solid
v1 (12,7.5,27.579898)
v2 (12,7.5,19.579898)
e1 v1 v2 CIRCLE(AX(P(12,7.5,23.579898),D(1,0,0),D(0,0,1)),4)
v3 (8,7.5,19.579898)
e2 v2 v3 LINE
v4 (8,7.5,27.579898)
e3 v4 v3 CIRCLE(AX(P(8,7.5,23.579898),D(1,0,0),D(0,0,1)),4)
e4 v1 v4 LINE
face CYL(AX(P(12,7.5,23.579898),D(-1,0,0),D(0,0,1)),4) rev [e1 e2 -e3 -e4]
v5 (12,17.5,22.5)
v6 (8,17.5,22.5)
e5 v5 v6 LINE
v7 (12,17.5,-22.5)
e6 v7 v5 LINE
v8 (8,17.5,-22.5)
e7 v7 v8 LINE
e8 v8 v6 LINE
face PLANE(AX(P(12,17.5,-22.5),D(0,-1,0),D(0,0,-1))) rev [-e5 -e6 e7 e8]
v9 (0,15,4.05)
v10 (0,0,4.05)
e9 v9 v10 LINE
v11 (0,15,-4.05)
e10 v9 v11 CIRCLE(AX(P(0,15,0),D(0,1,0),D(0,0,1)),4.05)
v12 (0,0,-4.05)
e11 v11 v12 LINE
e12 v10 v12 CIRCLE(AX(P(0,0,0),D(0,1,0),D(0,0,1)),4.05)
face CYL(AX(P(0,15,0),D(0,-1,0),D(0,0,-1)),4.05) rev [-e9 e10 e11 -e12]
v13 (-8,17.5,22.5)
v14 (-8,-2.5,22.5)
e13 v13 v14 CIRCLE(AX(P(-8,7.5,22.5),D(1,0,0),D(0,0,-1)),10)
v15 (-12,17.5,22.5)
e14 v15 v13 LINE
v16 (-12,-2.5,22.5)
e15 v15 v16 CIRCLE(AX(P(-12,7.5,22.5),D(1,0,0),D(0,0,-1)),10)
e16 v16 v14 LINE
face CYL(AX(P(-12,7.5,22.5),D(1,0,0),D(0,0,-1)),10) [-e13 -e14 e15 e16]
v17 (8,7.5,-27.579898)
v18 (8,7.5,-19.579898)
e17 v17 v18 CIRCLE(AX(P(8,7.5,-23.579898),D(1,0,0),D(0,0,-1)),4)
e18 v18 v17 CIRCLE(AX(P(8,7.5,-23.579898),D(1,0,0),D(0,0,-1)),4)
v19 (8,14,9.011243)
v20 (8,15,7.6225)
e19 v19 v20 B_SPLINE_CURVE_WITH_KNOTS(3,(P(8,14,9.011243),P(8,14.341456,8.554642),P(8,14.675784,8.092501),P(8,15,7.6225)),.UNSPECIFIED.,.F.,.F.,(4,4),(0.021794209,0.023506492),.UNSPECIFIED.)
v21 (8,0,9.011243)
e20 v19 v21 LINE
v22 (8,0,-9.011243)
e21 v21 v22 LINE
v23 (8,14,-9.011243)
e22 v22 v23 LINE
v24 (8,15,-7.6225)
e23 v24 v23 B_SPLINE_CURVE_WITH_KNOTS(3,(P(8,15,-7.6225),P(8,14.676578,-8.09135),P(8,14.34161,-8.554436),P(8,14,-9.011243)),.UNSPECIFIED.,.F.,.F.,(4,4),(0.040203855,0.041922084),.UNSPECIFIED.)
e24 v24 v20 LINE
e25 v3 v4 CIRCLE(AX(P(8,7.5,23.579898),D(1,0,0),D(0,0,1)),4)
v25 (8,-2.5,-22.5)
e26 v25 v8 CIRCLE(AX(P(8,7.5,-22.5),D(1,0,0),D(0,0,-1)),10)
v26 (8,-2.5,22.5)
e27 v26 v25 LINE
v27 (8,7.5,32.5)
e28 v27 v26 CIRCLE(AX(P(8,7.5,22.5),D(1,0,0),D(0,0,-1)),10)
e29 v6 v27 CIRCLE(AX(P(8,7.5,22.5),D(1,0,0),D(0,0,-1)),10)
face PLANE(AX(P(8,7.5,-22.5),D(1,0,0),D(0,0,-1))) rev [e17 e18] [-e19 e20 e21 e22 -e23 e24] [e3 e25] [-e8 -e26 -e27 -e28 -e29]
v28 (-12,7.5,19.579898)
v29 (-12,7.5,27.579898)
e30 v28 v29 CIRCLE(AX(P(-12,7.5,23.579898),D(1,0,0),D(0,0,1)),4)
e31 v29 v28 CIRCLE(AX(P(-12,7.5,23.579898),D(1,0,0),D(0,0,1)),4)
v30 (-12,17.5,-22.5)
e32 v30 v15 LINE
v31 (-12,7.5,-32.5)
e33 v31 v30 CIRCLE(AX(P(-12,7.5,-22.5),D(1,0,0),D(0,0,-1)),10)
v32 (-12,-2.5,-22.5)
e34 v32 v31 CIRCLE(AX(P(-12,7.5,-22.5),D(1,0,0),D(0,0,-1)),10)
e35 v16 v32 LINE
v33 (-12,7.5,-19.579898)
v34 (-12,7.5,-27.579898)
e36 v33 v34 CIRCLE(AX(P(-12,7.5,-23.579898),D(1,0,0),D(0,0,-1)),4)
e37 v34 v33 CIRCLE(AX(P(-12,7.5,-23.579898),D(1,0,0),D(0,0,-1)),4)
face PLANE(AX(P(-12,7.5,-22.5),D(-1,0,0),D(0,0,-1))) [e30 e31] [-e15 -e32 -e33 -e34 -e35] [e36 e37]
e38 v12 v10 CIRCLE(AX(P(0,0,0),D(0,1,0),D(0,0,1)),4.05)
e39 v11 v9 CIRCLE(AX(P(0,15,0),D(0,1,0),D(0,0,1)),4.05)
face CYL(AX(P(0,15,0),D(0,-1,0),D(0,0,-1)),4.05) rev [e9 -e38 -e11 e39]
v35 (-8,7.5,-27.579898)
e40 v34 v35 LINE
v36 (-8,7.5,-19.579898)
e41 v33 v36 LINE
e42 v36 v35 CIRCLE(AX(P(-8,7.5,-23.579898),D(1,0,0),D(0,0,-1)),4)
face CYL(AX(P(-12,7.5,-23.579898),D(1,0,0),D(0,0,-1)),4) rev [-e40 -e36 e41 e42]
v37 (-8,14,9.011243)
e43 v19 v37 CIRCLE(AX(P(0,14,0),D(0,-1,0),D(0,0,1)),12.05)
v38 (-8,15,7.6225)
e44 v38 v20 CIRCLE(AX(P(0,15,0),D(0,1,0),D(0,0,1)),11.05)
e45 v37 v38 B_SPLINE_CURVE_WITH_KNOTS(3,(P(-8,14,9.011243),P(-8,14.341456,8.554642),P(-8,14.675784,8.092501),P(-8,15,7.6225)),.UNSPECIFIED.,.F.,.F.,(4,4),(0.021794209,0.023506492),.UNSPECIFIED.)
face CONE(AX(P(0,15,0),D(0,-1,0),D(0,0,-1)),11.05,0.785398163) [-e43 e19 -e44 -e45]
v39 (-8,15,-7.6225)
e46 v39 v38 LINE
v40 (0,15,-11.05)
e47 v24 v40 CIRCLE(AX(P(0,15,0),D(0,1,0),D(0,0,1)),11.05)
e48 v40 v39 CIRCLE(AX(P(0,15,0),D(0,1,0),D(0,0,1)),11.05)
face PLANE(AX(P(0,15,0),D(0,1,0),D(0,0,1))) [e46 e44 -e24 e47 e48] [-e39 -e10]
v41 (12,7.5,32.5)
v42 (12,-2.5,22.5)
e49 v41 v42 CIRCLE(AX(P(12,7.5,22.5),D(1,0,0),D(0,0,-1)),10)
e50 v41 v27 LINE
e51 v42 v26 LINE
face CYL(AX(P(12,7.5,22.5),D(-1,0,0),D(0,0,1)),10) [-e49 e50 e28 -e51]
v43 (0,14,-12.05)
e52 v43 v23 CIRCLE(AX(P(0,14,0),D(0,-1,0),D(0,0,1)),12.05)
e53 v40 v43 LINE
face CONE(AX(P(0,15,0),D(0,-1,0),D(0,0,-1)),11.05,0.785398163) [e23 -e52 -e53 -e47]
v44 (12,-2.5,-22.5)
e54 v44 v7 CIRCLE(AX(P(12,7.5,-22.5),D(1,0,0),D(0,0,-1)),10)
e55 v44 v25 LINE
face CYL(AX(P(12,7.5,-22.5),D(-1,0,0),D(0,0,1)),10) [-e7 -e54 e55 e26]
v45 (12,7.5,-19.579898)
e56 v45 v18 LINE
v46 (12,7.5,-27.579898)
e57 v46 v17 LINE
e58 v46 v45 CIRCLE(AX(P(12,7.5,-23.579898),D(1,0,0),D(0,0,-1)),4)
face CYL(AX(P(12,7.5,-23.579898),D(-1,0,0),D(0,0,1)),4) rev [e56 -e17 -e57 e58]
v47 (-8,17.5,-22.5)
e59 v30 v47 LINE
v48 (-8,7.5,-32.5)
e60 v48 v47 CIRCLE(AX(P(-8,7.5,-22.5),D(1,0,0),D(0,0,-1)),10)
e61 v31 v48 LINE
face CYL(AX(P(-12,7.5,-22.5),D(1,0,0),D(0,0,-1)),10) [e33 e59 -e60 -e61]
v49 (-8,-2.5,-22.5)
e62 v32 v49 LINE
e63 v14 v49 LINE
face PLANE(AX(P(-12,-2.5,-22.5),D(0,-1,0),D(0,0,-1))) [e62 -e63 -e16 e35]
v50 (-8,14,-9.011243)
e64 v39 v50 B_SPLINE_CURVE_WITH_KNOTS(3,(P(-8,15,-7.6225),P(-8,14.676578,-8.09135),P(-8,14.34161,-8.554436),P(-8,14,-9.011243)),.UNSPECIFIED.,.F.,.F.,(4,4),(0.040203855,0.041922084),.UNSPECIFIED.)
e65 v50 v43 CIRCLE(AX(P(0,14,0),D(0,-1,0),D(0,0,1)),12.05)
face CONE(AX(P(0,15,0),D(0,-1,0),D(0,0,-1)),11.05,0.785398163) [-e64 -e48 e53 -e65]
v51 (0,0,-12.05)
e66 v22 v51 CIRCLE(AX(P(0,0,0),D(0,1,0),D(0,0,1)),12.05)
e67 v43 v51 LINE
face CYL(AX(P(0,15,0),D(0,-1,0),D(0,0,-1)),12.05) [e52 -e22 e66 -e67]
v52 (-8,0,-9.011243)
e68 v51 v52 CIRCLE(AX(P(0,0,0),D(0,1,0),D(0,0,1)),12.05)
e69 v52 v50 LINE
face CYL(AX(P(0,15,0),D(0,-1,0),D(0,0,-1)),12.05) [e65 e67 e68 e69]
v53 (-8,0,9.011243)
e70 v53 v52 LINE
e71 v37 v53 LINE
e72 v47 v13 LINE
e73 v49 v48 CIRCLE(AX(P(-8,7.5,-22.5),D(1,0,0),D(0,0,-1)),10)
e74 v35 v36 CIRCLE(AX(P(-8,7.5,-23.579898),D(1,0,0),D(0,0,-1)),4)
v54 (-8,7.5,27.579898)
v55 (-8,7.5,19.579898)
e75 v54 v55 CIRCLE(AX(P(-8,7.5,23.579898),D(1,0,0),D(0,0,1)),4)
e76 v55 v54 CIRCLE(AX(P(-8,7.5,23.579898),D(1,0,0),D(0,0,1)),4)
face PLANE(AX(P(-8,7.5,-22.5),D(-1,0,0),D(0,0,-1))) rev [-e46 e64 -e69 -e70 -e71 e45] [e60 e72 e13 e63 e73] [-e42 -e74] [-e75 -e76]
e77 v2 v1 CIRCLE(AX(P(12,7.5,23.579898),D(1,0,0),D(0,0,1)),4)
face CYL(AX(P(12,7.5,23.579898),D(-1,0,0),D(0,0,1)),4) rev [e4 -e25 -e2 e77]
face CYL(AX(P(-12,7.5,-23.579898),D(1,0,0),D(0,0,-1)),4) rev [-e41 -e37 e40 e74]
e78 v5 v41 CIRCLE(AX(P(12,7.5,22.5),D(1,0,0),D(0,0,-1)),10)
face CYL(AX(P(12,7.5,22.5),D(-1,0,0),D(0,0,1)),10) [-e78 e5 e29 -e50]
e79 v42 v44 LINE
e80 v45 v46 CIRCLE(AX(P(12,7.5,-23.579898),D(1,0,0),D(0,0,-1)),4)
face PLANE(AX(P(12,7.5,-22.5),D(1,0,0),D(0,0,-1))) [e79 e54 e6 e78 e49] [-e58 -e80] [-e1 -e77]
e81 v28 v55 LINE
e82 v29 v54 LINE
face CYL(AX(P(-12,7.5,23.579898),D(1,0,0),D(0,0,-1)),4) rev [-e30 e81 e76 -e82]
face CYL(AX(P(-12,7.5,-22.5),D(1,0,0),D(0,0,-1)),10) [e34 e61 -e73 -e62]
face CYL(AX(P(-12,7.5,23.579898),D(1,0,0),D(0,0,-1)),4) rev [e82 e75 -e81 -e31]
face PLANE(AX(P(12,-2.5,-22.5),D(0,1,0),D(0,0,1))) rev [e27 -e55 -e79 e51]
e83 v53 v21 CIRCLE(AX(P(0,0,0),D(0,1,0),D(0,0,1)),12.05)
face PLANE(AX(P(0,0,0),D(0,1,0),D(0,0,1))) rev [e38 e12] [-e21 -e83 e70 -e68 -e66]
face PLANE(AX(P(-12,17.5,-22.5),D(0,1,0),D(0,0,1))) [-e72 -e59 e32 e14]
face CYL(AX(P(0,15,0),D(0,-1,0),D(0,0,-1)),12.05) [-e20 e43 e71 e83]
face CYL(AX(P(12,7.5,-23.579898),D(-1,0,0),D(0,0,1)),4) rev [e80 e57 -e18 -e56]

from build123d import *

# Parameters (mm, degrees)
SKETCH1_R          = 12.05
SKETCH1_R_2        = 4.05
BOSS_EXTRU_1_DEPTH = 15
CHAMFER1_SIZE      = 1
CUT_EXTRUDE1_REACH = 24.703
SKETCH5_W          = 7
SKETCH5_H          = 40.880501257
SKETCH6_R          = 4
BOSS_EXTRU_4_DEPTH = 4


with BuildPart() as part:
    # Sketch1 → Boss.-Extru.1 (new body)
    with BuildSketch(Plane(origin=(0, 0, 0), x_dir=(1, 0, 0), z_dir=(0, 1, 0))):
        with Locations(Location((0, 0, 0), (0, 0, 270))):
            Circle(SKETCH1_R)
        with Locations(Location((0, 0, 0), (0, 0, 270))):
            Circle(SKETCH1_R_2, mode=Mode.SUBTRACT)
    extrude(amount=BOSS_EXTRU_1_DEPTH)

    # Chamfer1
    chamfer1_edges = [part.edges().sort_by_distance(p)[0] for p in [
        (0, 15, -12.05),
    ]]
    chamfer(chamfer1_edges, length=CHAMFER1_SIZE)

    # Sketch5 → Cut-Extrude1 (cut, up to next)
    with BuildSketch(Plane(origin=(0, 15, 0), x_dir=(1, 0, 0), z_dir=(0, 1, 0)), mode=Mode.PRIVATE) as cut_extrude1_sk1:
        with Locations((11.5, -1.662295536)):
            Rectangle(SKETCH5_W, SKETCH5_H)
    cut_extrude1_tool1 = extrude(cut_extrude1_sk1.sketch, amount=-CUT_EXTRUDE1_REACH, mode=Mode.PRIVATE) & part.part
    # Sketch5 → Cut-Extrude1 (cut, up to next)
    with BuildSketch(Plane(origin=(0, 15, 0), x_dir=(1, 0, 0), z_dir=(0, 1, 0)), mode=Mode.PRIVATE) as cut_extrude1_sk2:
        with Locations((-11.5, -1.662295536)):
            Rectangle(SKETCH5_W, SKETCH5_H)
    cut_extrude1_tool2 = extrude(cut_extrude1_sk2.sketch, amount=-CUT_EXTRUDE1_REACH, mode=Mode.PRIVATE) & part.part
    add(cut_extrude1_tool1.solids().sort_by_distance((11.5, 15, 1.662296))[0], mode=Mode.SUBTRACT)
    add(cut_extrude1_tool2.solids().sort_by_distance((-11.5, 15, 1.662296))[0], mode=Mode.SUBTRACT)

    # Sketch6 → Boss.-Extru.4 (add)
    with BuildSketch(Plane(origin=(8, 0, 0), x_dir=(0, 0, -1), z_dir=(1, 0, 0))):
        with BuildLine():
            Line((22.5, -2.5), (-22.5, -2.5))
            ThreePointArc((-22.5, -2.5), (-32.5, 7.5), (-22.5, 17.5))
            Line((-22.5, 17.5), (22.5, 17.5))
            ThreePointArc((22.5, 17.5), (32.5, 7.5), (22.5, -2.5))
        make_face()
        with Locations((23.579898115, 7.5)):
            Circle(SKETCH6_R, mode=Mode.SUBTRACT)
        with Locations(Location((-23.579898115, 7.5, 0), (0, 0, 180))):
            Circle(SKETCH6_R, mode=Mode.SUBTRACT)
    boss_extru_4 = extrude(amount=BOSS_EXTRU_4_DEPTH)

    # Mirror1: Boss.-Extru.4 across plane
    add(boss_extru_4.mirror(Plane(origin=(0, 0, 0), x_dir=(0, 0, 1), z_dir=(1, 0, 0))))


solid = part.part
